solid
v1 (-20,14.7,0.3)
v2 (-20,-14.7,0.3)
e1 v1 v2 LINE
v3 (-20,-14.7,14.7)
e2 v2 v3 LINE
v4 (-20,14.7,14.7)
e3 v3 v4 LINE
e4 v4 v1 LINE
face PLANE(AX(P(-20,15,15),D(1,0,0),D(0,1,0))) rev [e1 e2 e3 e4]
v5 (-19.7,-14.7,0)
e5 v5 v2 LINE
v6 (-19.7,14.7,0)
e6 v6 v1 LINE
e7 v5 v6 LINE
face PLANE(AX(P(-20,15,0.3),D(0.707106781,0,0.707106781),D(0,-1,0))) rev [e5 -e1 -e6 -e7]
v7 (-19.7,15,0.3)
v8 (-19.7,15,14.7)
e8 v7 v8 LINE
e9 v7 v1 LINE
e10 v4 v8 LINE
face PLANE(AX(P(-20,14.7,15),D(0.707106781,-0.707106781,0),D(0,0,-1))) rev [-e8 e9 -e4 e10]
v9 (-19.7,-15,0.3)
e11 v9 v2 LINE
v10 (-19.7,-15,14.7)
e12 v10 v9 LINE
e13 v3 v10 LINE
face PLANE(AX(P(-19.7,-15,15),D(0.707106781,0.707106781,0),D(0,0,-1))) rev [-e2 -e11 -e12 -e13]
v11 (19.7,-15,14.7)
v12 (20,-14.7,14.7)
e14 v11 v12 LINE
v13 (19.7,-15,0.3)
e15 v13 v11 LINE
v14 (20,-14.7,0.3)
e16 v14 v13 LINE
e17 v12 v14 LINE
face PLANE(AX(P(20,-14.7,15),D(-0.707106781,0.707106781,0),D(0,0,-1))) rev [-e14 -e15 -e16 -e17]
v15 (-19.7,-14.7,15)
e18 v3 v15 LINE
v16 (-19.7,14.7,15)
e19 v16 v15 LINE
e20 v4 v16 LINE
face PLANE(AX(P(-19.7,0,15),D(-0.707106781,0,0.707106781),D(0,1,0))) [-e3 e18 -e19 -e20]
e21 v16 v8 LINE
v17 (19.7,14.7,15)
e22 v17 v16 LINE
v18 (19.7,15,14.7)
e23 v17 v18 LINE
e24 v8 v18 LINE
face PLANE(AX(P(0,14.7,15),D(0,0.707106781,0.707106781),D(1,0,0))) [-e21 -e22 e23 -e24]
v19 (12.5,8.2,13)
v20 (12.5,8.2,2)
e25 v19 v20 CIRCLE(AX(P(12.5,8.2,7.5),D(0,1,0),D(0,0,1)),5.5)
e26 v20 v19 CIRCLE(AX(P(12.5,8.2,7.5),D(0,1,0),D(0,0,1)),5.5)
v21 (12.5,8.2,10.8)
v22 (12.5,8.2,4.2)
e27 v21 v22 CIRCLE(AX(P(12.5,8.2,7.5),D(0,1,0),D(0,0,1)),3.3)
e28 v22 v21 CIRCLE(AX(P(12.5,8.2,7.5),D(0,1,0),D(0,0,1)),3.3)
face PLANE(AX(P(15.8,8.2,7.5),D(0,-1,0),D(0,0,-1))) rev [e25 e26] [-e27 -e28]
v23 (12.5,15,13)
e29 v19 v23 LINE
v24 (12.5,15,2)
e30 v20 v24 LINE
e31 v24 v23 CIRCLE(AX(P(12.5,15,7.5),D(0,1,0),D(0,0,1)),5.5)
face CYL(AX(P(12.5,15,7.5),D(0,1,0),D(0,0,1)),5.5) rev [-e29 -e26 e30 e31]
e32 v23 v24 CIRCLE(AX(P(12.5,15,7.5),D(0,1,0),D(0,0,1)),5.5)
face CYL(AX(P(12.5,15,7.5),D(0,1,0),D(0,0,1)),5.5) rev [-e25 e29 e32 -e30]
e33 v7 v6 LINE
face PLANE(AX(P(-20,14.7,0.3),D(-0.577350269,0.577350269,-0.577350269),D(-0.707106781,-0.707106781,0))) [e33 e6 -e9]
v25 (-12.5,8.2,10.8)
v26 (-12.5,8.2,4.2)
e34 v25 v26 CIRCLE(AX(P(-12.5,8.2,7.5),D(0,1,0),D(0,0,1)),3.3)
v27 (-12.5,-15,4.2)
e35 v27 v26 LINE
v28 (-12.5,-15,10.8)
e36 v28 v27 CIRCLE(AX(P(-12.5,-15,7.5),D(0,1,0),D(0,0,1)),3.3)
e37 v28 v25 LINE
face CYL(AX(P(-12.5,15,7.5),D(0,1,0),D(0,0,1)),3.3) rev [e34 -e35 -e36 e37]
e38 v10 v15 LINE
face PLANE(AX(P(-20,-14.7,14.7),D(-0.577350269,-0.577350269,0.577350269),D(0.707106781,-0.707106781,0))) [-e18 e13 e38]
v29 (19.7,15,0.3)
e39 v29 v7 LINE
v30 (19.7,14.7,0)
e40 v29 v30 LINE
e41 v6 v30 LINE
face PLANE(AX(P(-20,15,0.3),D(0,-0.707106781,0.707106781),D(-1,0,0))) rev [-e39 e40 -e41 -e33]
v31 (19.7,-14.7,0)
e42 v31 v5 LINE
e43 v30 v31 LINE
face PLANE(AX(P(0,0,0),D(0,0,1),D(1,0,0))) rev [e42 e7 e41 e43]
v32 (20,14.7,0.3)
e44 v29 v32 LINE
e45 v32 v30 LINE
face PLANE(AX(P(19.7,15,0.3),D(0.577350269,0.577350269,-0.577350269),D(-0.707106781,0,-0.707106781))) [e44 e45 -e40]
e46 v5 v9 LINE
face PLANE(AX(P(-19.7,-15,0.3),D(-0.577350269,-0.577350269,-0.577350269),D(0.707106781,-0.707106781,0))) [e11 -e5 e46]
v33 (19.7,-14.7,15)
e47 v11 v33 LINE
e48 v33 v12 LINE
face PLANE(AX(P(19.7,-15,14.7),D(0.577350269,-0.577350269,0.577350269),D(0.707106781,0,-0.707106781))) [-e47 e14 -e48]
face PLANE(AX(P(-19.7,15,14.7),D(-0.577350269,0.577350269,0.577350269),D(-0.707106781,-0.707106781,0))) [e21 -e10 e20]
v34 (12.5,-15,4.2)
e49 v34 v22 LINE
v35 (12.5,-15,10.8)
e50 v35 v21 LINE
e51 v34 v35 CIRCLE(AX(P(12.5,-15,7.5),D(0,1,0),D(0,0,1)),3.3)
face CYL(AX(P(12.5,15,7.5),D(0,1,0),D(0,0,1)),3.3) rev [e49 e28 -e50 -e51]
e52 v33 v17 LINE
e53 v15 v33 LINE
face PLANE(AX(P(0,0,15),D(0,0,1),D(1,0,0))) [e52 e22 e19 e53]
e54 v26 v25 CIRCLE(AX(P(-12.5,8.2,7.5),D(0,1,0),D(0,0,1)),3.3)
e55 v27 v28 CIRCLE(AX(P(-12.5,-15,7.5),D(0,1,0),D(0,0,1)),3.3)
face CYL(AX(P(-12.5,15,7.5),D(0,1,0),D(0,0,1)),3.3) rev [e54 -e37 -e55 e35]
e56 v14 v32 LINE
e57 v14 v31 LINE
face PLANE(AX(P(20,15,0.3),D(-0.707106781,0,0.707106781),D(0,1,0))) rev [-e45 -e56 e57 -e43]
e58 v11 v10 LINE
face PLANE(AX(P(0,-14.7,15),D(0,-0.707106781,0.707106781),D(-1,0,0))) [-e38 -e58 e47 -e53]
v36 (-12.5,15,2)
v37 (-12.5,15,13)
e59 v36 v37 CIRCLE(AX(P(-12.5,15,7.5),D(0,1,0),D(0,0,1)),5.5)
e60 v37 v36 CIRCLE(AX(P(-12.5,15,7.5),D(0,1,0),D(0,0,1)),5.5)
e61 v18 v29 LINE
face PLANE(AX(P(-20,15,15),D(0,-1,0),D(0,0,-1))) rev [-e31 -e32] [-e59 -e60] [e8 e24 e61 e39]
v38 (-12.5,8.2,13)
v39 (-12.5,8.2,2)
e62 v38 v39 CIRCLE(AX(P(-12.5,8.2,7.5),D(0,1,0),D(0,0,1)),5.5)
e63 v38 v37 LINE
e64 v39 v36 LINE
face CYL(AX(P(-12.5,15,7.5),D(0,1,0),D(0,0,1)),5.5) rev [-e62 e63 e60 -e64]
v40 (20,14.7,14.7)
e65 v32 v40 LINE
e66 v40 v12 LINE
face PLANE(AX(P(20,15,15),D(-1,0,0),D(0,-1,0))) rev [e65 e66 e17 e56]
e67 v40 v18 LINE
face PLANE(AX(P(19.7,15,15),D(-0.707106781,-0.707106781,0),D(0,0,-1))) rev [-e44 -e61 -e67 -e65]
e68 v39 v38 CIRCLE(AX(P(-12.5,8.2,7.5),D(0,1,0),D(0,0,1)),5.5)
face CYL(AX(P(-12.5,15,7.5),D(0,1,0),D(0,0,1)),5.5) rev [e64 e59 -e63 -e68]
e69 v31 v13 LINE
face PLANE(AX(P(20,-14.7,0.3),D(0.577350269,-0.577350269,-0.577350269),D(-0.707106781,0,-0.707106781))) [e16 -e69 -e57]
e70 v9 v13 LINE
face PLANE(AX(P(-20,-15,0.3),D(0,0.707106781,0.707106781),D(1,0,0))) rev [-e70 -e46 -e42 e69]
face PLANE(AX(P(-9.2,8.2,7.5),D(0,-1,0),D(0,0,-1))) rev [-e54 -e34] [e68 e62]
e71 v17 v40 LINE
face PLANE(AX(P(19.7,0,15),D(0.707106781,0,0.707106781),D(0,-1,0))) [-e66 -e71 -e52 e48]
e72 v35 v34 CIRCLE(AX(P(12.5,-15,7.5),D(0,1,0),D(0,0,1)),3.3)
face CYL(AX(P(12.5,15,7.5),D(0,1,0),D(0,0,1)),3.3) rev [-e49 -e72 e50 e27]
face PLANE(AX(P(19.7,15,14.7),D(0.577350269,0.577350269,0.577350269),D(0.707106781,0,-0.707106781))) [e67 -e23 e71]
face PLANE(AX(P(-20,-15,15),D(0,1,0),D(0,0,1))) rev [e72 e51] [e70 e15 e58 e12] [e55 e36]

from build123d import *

# Parameters (mm, degrees)
SKETCH_1_W                = 40
SKETCH_1_H                = 30
EXTRUDE_1_DEPTH           = 15
HOLE_WIZARD_1_D           = 6.6
HOLE_WIZARD_1_CBORE_D     = 11
HOLE_WIZARD_1_CBORE_DEPTH = 6.8
CHAMFER_1_SIZE            = 0.3


with BuildPart() as part:
    # 草图1 → 凸台-拉伸1 (new body)
    with BuildSketch(Plane.XY):
        Rectangle(SKETCH_1_W, SKETCH_1_H)
    extrude(amount=EXTRUDE_1_DEPTH)

    # 打孔尺寸根据内六角圆柱头螺钉的类型1 (through all)
    with Locations(Plane(origin=(0, 15, 0), x_dir=(1, 0, 0), z_dir=(0, 1, 0))):
        with Locations((-12.5, -7.5), (12.5, -7.5)):
            CounterBoreHole(HOLE_WIZARD_1_D / 2, HOLE_WIZARD_1_CBORE_D / 2, HOLE_WIZARD_1_CBORE_DEPTH)

    # 倒角1
    chamfer_1_edges = [part.edges().sort_by_distance(p)[0] for p in [
        (-20, 0, 15),
        (0, -15, 15),
        (20, 0, 15),
        (0, -15, 0),
        (-20, 0, 0),
        (0, 15, 0),
        (20, 0, 0),
        (0, 15, 15),
        (20, -15, 7.5),
        (-20, -15, 7.5),
        (-20, 15, 7.5),
        (20, 15, 7.5),
    ]]
    chamfer(chamfer_1_edges, length=CHAMFER_1_SIZE)


solid = part.part
